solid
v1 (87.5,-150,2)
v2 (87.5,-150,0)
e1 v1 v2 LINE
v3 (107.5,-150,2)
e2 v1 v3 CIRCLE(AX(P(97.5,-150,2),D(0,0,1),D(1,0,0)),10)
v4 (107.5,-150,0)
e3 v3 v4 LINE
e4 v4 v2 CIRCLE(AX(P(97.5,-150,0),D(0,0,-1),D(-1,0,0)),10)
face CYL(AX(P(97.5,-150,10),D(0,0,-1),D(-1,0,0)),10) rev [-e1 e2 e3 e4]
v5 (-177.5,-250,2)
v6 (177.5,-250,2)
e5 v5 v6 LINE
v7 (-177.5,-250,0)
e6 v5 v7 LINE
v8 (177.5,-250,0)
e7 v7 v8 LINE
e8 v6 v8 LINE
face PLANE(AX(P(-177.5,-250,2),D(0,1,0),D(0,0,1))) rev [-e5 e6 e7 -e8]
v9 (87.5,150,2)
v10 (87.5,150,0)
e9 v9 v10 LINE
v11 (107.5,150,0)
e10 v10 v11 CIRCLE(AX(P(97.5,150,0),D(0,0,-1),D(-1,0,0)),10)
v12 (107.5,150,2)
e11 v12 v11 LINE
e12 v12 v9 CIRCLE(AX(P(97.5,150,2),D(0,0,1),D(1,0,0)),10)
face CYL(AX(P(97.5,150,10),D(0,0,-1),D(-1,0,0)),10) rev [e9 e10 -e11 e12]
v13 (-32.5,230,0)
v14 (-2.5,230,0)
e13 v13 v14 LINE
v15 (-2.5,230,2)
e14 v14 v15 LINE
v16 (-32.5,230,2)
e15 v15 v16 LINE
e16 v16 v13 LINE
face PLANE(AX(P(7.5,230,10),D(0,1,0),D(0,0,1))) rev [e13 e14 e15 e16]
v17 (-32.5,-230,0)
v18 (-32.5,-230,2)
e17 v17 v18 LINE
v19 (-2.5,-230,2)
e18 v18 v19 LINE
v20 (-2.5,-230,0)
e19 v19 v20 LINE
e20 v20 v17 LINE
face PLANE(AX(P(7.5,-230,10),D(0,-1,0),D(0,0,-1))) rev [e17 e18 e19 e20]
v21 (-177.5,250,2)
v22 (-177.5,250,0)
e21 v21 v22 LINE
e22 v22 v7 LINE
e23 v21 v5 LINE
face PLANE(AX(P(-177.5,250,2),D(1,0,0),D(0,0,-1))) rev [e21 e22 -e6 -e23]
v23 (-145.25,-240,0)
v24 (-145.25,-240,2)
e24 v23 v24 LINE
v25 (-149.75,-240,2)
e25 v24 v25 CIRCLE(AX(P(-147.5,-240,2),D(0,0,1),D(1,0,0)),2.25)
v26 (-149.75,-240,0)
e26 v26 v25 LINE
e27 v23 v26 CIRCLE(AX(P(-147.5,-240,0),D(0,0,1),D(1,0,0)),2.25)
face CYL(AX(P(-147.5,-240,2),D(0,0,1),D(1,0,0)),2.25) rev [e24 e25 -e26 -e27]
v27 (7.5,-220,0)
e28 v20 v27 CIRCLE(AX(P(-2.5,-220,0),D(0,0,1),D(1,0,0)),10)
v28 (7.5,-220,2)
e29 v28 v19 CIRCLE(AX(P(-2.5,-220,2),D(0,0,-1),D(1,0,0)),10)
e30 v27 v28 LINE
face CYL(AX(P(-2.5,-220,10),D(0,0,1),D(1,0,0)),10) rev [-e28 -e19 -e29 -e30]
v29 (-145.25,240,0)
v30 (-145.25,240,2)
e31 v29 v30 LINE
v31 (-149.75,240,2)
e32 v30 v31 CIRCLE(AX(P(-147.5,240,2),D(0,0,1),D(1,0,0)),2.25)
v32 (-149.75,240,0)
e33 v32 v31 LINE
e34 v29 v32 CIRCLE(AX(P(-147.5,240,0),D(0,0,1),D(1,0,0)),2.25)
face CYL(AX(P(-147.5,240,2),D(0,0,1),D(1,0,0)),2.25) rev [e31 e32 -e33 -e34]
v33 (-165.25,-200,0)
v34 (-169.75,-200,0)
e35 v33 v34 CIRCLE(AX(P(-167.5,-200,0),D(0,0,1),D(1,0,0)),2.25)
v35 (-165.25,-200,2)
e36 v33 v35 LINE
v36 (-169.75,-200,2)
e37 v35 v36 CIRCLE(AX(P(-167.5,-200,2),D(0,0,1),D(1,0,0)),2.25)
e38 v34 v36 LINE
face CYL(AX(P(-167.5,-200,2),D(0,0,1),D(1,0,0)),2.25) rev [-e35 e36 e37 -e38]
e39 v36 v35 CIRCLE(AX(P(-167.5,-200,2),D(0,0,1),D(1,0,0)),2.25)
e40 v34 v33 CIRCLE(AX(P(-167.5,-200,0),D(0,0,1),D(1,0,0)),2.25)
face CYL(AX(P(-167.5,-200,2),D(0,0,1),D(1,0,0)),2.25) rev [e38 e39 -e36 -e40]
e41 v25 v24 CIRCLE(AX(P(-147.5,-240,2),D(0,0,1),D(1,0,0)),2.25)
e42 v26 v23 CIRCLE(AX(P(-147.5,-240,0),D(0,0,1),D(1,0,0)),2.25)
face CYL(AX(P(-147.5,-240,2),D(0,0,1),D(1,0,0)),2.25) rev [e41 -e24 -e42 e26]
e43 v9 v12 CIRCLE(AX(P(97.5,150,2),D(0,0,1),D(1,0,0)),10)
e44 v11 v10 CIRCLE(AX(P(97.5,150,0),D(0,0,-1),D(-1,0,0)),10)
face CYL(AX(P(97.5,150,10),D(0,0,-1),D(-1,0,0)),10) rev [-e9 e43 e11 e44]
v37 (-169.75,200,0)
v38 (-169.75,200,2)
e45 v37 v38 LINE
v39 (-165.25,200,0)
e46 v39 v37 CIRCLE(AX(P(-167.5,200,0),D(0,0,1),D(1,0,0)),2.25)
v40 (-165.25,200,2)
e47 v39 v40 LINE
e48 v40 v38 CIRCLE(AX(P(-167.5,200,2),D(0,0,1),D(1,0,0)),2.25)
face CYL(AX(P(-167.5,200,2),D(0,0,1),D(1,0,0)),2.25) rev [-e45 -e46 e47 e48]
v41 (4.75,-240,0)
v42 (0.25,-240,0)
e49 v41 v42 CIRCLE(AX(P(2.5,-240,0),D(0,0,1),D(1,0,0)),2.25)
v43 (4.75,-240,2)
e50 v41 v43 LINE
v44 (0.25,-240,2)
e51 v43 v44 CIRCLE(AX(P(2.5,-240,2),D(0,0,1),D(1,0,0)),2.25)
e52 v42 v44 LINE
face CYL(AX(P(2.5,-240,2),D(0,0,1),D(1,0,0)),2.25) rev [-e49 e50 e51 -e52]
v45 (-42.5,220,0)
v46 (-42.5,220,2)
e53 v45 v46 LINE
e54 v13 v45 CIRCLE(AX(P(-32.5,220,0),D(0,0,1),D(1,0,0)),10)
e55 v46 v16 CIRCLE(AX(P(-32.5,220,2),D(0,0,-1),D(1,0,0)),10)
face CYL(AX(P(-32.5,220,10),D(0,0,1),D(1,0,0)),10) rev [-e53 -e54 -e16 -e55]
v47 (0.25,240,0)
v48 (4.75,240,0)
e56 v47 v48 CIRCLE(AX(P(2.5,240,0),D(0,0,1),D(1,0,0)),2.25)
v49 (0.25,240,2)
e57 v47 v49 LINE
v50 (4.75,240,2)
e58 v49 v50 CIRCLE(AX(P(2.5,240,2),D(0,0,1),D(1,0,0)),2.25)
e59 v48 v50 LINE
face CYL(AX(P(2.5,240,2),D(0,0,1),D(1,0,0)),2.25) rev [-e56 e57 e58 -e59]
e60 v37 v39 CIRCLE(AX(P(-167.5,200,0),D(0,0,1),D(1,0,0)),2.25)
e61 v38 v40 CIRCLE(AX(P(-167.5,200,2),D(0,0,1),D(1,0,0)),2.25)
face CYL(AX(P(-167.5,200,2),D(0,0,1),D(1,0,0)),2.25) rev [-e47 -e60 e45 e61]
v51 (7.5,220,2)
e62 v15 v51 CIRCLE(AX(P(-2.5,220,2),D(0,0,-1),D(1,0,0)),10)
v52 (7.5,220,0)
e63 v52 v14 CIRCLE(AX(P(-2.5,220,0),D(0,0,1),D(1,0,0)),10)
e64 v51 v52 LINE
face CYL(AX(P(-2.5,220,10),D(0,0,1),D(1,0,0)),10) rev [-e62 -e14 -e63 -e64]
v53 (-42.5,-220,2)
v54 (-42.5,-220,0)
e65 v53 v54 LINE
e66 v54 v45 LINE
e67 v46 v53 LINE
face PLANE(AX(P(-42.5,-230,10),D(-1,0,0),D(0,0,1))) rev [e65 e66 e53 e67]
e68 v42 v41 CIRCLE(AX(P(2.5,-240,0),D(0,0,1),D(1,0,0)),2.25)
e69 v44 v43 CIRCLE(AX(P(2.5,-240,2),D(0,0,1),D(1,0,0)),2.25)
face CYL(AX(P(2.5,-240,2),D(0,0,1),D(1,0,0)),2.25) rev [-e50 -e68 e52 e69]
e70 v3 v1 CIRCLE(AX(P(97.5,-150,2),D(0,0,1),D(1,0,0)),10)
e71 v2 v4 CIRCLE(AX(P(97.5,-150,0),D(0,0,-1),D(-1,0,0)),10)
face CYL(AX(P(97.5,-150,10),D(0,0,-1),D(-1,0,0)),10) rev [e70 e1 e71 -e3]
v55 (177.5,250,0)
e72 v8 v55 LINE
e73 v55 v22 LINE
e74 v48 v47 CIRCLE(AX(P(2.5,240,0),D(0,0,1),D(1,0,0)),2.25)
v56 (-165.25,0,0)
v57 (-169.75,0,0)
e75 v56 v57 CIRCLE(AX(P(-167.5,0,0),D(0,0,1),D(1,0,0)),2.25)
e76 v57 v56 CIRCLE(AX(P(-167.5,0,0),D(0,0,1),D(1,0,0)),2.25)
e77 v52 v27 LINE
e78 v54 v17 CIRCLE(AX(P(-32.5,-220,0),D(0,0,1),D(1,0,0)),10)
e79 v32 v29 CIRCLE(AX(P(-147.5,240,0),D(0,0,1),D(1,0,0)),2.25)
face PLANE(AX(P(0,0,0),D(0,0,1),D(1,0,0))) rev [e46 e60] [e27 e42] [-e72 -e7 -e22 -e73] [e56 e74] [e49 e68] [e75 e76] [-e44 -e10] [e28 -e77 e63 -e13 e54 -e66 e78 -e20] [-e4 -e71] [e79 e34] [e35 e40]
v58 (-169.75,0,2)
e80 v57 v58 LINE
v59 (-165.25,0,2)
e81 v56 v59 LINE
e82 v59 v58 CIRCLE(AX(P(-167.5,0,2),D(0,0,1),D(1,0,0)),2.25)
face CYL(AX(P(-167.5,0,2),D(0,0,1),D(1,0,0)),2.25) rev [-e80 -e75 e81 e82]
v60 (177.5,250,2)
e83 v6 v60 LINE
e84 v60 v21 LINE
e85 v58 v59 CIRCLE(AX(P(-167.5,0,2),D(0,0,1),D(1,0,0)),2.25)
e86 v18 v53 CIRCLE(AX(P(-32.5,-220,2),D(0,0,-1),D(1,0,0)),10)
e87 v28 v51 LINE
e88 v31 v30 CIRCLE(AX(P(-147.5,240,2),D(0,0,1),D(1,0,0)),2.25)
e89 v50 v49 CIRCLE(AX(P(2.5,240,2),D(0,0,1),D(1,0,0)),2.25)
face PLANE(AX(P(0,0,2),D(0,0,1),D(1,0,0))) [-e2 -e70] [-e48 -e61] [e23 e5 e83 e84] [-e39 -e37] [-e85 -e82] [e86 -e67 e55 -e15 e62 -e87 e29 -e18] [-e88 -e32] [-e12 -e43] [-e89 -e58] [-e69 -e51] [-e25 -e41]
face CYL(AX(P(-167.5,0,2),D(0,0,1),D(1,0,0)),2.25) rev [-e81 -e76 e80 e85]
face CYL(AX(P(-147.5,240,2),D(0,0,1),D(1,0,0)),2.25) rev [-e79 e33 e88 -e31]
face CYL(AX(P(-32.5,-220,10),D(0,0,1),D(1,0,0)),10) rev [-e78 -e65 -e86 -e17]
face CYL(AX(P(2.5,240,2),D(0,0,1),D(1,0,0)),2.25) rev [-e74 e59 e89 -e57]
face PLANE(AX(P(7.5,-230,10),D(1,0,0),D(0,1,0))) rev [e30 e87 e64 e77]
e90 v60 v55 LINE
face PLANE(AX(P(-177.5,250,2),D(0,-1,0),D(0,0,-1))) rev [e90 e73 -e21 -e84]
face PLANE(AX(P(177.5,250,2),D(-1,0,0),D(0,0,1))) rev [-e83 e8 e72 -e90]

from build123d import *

# Parameters (mm, degrees)
SKETCH_1_W                  = 355
SKETCH_1_H                  = 500
EXTRUDE_1_DEPTH             = 2
HOLE_WIZARD_4_5_4_5_1_D     = 4.5
HOLE_WIZARD_4_5_4_5_1_DEPTH = 8
HOLE_WIZARD_4_5_4_5_1_TIP   = 1.351936393
SKETCH_4_W                  = 50
SKETCH_4_H                  = 460
CUT_EXTRUDE_1_DEPTH         = 10
FILLET_1_R                  = 10
SKETCH_5_R                  = 10
CUT_EXTRUDE_2_DEPTH         = 10


with BuildPart() as part:
    # 草图1 → 凸台-拉伸1 (new body)
    with BuildSketch(Plane.XY):
        Rectangle(SKETCH_1_W, SKETCH_1_H)
    extrude(amount=EXTRUDE_1_DEPTH)

    # Ø4.5 (4.5) 直径孔1
    with Locations(Plane.XY.offset(2)):
        with Locations((-147.5, -240), (-167.5, 0), (-167.5, 200), (-167.5, -200), (-147.5, 240), (2.5, 240), (2.5, -240)):
            Hole(HOLE_WIZARD_4_5_4_5_1_D / 2, depth=HOLE_WIZARD_4_5_4_5_1_DEPTH)
            with Locations((0, 0, -(HOLE_WIZARD_4_5_4_5_1_DEPTH + HOLE_WIZARD_4_5_4_5_1_TIP / 2))):  # 118° drill point
                Cone(0, HOLE_WIZARD_4_5_4_5_1_D / 2, HOLE_WIZARD_4_5_4_5_1_TIP, mode=Mode.SUBTRACT)

    # 草图4 → 切除-拉伸1 (cut)
    with BuildSketch(Plane(origin=(0, 0, 0), x_dir=(-1, 0, 0), z_dir=(0, 0, -1))):
        with Locations((17.5, 0)):
            Rectangle(SKETCH_4_W, SKETCH_4_H)
    extrude(amount=-CUT_EXTRUDE_1_DEPTH, mode=Mode.SUBTRACT)

    # 圆角1
    fillet_1_edges = [part.edges().sort_by_distance(p)[0] for p in [
        (-42.5, 230, 1),
        (-42.5, -230, 1),
        (7.5, -230, 1),
        (7.5, 230, 1),
    ]]
    fillet(fillet_1_edges, radius=FILLET_1_R)

    # 草图5 → 切除-拉伸2 (cut)
    with BuildSketch(Plane(origin=(0, 0, 0), x_dir=(-1, 0, 0), z_dir=(0, 0, -1))):
        with Locations((-97.5, -150)):
            Circle(SKETCH_5_R)
        with Locations((-97.5, 150)):
            Circle(SKETCH_5_R)
    extrude(amount=-CUT_EXTRUDE_2_DEPTH, mode=Mode.SUBTRACT)


solid = part.part
